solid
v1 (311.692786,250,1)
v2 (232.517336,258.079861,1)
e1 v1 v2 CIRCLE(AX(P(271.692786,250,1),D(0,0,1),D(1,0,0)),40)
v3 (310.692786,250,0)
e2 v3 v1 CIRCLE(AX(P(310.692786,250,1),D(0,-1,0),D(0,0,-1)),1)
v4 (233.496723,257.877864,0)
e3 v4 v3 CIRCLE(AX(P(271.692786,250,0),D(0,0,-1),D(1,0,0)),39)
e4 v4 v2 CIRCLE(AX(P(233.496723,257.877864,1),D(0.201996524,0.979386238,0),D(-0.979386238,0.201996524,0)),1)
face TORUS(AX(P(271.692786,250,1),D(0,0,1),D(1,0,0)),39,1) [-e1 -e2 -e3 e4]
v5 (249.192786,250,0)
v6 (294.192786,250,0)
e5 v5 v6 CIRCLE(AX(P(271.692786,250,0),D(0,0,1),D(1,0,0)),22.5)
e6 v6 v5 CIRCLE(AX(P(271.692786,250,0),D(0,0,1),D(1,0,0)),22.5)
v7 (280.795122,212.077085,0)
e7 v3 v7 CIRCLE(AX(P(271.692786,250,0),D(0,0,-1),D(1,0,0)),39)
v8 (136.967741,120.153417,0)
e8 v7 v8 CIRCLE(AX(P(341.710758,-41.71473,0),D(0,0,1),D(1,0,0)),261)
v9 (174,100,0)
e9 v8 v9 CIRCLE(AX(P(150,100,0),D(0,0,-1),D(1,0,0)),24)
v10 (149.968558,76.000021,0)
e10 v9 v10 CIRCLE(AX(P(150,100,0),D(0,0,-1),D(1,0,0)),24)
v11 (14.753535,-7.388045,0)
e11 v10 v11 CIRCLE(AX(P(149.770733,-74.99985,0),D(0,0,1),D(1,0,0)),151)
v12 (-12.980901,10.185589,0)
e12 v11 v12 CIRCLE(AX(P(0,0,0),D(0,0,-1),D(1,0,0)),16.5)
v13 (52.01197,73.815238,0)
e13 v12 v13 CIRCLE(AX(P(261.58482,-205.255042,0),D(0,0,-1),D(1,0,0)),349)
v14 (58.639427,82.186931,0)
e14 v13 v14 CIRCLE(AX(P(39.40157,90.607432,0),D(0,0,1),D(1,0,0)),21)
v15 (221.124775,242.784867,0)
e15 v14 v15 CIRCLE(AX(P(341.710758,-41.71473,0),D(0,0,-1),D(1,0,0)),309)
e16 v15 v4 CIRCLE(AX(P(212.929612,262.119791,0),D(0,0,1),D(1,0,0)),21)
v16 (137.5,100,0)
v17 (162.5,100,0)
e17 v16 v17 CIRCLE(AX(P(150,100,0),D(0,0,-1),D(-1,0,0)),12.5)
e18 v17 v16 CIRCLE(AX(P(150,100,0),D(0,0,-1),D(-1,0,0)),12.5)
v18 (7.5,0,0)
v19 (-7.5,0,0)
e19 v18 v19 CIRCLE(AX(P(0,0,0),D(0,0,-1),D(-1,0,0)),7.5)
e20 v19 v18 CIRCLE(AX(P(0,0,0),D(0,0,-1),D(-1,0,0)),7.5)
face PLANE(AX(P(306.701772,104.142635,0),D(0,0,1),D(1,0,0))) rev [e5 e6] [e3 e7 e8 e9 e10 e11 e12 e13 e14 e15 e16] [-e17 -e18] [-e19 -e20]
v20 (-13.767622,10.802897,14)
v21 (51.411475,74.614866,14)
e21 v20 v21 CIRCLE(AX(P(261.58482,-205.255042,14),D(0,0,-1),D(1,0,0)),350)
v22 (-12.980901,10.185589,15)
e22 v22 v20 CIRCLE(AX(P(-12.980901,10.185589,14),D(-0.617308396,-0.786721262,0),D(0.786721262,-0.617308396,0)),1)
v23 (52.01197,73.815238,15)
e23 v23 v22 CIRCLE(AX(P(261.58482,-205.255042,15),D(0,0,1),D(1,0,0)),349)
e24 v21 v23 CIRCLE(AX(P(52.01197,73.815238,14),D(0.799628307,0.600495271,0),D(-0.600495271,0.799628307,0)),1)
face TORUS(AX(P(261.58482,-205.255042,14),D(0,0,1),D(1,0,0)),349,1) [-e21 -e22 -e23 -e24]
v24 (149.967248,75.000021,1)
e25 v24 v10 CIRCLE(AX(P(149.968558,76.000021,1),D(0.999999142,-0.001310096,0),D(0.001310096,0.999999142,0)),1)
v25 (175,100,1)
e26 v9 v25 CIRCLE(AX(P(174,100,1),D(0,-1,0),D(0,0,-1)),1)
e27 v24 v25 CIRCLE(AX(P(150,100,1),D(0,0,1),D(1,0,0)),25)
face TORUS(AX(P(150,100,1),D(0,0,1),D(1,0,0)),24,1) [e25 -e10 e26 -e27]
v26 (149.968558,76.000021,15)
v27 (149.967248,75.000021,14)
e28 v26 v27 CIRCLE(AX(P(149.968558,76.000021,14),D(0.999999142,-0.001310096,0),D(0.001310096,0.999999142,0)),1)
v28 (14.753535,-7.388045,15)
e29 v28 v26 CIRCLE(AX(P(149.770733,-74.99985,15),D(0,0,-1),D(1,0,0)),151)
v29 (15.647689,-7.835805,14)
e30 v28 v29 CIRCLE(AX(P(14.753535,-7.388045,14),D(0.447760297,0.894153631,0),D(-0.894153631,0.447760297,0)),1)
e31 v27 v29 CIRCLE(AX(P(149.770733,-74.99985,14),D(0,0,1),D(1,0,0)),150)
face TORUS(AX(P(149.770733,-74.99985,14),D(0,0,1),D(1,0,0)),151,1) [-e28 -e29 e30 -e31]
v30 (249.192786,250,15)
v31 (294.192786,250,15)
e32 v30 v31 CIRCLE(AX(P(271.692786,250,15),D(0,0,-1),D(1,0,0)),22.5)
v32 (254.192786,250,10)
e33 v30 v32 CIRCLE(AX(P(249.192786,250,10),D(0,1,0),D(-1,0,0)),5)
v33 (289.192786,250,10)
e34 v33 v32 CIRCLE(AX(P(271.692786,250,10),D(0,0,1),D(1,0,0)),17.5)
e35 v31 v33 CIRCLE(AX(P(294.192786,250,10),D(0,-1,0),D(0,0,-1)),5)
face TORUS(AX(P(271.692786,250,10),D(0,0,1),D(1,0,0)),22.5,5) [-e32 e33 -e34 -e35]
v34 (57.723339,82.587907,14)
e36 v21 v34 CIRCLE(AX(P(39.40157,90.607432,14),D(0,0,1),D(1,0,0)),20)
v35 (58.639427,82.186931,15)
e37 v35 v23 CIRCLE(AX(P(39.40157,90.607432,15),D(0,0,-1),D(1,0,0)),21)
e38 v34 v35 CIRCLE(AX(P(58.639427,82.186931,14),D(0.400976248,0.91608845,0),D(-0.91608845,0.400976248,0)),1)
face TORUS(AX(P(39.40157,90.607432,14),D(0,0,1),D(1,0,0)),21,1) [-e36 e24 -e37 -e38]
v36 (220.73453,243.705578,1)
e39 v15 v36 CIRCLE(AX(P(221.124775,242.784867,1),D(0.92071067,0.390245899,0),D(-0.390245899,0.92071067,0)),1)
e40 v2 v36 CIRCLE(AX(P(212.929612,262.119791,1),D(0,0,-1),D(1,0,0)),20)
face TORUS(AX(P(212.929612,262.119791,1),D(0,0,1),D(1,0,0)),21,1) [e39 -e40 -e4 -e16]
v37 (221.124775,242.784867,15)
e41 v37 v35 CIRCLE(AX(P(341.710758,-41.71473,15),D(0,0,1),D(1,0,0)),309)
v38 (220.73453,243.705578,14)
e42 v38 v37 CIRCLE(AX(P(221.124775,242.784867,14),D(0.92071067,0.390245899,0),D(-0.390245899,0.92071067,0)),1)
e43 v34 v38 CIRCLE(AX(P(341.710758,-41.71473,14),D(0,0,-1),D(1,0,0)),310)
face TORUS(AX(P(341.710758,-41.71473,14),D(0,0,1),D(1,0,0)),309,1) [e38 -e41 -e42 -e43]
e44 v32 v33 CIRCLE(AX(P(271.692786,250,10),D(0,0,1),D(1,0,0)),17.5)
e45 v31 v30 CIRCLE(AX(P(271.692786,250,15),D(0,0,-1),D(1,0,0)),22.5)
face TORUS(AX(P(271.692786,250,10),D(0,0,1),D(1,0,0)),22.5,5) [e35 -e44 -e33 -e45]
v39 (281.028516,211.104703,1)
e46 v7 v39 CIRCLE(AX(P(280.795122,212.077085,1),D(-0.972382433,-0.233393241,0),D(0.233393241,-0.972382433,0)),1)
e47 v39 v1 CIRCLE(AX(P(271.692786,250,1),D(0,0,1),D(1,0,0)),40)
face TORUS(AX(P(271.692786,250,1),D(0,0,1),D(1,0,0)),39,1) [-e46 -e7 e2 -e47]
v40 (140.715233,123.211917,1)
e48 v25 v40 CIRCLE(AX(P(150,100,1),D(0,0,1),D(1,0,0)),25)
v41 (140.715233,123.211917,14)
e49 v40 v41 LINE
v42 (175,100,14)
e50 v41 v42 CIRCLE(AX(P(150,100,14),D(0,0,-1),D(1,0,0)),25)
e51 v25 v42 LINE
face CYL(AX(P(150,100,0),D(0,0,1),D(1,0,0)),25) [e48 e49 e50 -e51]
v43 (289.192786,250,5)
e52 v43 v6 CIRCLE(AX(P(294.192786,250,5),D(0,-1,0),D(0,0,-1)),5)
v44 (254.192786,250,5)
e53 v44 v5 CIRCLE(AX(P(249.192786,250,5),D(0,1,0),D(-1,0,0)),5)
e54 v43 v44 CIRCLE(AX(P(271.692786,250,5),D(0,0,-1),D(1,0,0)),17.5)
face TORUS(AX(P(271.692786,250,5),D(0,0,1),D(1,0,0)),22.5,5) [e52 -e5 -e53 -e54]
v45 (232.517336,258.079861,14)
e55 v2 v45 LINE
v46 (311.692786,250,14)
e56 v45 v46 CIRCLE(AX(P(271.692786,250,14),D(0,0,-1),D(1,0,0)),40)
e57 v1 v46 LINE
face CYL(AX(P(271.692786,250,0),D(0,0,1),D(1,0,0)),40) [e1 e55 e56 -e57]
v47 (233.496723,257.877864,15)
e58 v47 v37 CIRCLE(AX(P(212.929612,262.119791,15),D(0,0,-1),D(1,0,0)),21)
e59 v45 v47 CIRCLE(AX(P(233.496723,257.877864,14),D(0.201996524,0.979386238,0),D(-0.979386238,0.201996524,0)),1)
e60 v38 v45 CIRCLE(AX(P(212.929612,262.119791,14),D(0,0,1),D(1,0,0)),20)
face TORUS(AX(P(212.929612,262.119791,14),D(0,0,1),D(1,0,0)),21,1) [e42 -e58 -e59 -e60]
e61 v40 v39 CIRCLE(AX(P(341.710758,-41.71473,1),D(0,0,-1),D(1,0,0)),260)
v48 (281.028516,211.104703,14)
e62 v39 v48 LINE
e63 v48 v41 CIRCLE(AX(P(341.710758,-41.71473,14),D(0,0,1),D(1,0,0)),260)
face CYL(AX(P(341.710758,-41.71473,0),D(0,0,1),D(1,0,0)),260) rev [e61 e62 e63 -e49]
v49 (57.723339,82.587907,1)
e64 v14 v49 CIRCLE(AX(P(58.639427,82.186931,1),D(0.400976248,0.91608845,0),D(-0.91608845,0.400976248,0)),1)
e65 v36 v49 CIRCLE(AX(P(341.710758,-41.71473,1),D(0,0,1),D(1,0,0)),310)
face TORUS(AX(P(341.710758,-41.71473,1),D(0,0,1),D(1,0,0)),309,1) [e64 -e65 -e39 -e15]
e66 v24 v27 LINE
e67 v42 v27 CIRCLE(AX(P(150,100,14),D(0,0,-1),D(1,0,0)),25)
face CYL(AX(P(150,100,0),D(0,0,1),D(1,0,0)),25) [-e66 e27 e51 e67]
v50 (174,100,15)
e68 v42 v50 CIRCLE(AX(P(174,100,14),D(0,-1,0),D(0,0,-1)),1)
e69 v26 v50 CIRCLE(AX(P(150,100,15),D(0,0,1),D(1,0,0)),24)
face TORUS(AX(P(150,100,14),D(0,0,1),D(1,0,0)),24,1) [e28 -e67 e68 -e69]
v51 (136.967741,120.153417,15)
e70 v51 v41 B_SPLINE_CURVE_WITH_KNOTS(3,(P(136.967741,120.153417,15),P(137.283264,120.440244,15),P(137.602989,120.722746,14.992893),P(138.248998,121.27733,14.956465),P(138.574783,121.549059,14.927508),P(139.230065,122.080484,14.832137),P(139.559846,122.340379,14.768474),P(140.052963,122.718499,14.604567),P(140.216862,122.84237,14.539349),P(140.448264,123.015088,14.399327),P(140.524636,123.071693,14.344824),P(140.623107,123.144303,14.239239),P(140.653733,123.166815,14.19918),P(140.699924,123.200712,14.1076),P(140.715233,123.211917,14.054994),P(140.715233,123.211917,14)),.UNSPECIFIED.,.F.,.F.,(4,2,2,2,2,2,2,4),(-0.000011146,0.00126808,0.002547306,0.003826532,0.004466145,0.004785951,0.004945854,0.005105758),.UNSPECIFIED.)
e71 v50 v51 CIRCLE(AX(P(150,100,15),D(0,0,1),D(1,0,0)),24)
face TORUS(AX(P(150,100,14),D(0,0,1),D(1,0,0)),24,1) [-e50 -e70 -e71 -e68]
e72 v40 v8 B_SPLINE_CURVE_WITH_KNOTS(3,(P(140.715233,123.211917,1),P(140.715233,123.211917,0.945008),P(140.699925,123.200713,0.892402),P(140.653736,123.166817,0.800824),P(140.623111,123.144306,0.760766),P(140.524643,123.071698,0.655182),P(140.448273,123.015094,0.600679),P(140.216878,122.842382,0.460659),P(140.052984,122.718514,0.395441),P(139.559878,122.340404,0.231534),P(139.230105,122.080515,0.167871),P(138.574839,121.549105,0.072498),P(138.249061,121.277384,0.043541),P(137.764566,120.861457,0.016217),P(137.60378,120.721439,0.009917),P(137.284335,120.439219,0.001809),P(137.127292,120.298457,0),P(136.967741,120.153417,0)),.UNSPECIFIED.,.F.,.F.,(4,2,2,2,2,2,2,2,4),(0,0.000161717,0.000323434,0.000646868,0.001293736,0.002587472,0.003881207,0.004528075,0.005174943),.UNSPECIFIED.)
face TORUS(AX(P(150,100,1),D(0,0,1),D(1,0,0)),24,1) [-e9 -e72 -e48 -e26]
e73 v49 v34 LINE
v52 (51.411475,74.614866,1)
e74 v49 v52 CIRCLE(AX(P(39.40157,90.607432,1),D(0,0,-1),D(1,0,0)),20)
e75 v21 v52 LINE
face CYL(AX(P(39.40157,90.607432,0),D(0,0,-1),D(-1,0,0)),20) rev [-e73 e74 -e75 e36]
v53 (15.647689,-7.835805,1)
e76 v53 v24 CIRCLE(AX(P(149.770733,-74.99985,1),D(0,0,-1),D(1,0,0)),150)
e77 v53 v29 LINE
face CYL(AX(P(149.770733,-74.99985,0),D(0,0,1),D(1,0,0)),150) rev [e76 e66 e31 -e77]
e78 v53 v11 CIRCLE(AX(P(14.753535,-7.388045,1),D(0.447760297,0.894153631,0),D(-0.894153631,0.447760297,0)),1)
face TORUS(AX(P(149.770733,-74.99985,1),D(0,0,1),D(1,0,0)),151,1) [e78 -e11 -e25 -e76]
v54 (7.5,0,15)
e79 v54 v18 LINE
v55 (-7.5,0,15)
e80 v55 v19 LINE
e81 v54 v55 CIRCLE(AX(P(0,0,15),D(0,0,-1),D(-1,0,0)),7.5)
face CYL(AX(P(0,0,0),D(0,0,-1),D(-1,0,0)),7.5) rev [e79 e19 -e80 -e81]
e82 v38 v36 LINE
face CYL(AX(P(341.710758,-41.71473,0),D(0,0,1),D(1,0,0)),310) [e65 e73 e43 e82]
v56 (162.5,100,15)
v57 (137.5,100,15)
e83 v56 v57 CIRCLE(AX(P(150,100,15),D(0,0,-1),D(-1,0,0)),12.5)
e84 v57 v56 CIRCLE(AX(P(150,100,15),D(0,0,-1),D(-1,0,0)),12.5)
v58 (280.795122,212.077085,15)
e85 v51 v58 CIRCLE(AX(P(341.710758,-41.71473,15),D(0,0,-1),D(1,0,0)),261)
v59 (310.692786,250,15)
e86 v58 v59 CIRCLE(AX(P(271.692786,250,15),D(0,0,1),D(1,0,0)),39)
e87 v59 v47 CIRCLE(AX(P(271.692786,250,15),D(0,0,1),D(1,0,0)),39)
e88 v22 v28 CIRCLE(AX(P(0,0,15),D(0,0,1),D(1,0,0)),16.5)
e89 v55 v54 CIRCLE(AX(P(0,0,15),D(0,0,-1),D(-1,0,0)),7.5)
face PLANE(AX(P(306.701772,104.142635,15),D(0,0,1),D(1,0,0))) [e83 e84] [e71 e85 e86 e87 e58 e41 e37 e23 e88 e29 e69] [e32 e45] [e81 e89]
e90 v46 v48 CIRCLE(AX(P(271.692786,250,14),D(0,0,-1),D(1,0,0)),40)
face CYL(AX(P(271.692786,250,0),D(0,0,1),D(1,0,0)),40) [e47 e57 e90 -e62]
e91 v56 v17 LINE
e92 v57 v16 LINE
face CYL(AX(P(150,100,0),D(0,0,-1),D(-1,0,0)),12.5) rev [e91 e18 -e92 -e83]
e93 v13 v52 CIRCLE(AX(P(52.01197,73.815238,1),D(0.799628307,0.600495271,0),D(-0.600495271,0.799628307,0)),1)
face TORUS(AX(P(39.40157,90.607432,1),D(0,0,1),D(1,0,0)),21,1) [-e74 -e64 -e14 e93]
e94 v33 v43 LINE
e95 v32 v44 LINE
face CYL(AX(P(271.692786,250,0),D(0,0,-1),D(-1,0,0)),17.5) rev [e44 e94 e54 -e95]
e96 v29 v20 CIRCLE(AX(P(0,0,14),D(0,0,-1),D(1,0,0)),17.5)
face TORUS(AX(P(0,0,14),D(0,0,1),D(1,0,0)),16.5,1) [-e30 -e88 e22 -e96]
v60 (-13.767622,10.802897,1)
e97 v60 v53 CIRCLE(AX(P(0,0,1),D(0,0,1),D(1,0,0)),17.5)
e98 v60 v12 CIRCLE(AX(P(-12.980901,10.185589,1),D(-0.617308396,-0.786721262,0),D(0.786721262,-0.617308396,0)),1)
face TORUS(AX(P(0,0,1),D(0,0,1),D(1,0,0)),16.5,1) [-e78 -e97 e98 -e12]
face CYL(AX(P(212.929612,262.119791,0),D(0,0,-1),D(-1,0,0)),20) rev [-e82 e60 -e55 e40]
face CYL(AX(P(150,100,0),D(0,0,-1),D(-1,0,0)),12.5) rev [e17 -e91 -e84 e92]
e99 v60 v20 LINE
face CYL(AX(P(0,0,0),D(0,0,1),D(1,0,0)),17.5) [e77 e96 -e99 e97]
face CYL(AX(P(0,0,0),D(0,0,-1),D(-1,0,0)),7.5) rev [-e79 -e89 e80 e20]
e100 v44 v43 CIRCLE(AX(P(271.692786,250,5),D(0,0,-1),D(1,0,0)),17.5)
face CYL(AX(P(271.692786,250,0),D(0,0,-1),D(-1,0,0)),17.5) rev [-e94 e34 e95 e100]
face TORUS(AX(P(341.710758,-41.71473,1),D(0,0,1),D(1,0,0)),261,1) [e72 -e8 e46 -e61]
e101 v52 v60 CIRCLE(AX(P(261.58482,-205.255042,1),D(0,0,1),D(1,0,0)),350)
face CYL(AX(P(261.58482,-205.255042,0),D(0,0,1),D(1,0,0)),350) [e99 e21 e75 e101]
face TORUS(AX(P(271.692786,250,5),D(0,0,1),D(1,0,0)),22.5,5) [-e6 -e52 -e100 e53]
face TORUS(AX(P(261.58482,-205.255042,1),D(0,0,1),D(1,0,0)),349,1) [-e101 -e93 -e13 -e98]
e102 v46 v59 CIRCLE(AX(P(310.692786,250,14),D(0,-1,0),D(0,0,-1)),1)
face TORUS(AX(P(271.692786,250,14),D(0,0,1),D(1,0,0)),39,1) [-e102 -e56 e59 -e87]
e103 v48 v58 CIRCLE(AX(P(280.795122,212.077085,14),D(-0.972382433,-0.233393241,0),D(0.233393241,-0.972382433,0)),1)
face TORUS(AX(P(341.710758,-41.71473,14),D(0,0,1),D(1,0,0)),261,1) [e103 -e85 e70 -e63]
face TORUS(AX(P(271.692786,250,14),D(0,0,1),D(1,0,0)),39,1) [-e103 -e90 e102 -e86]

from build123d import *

# Parameters (mm, degrees)
BOSS_EXTRUDE1_DEPTH        = 15
M30_CLEARANCE_HOLE1_D      = 35
F_25_0_25_DIAMETER_HOLE1_D = 25
F_15_0_15_DIAMETER_HOLE1_D = 15
FILLET1_R                  = 20
FILLET2_R                  = 1
FILLET3_R                  = 5


with BuildPart() as part:
    # Sketch1 → Boss-Extrude1 (new body)
    with BuildSketch(Plane.XY.offset(15)):
        with BuildLine():
            ThreePointArc((231.736862835, 248.122711482), (126.150277633, 181.071444034), (55.655412109, 77.752165214))
            ThreePointArc((55.655412109, 77.752165214), (18.626786765, 46.68025613), (-13.767622093, 10.802896922))
            ThreePointArc((-13.767622093, 10.802896922), (-9.366641165, -14.782287823), (15.647688545, -7.835805205))
            ThreePointArc((15.647688545, -7.835805205), (71.03368715, 52.673473852), (149.967247602, 75.000021454))
            ThreePointArc((149.967247602, 75.000021454), (174.552001265, 104.711606298), (140.715233091, 123.211917272))
            ThreePointArc((140.715233091, 123.211917272), (203.688662251, 178.625691043), (281.028515533, 211.104702698))
            ThreePointArc((281.028515533, 211.104702698), (295.713241867, 281.984647802), (231.736862835, 248.122711482))
        make_face()
    extrude(amount=-BOSS_EXTRUDE1_DEPTH)

    # M30 Clearance Hole1 (through all)
    with Locations(Plane(origin=(0, 0, 0), x_dir=(-1, 0, 0), z_dir=(0, 0, -1))):
        with Locations((-271.692785898, 250)):
            Hole(M30_CLEARANCE_HOLE1_D / 2)

    # Ø25.0 (25) Diameter Hole1 (through all)
    with Locations(Plane(origin=(0, 0, 0), x_dir=(-1, 0, 0), z_dir=(0, 0, -1))):
        with Locations((-150, 100)):
            Hole(F_25_0_25_DIAMETER_HOLE1_D / 2)

    # Ø15.0 (15) Diameter Hole1 (through all)
    with Locations(Plane(origin=(0, 0, 0), x_dir=(-1, 0, 0), z_dir=(0, 0, -1))):
        with Locations((0, 0)):
            Hole(F_15_0_15_DIAMETER_HOLE1_D / 2)

    # Fillet1
    fillet1_edges = [part.edges().sort_by_distance(p)[0] for p in [
        (55.655412109, 77.752165214, 7.5),
        (231.736862835, 248.122711482, 7.5),
    ]]
    fillet(fillet1_edges, radius=FILLET1_R)

    # Fillet2
    fillet2_edges = [part.edges().sort_by_distance(p)[0] for p in [
        (299.518468185, 278.735542543, 15),
        (-9.366641165, -14.782287823, 0),
        (71.03368715, 52.673473852, 0),
        (174.552001265, 104.711606298, 0),
        (203.688662251, 178.625691043, 0),
        (123.791931468, 178.765167219, 15),
        (123.791931468, 178.765167219, 0),
        (16.734224094, 44.841311513, 15),
        (16.734224094, 44.841311513, 0),
        (228.397133093, 249.440841249, 15),
        (228.397133093, 249.440841249, 0),
        (55.082608051, 78.193527318, 15),
        (55.082608051, 78.193527318, 0),
        (299.518468185, 278.735542543, 0),
        (203.688662251, 178.625691043, 15),
        (174.552001265, 104.711606298, 15),
        (71.03368715, 52.673473852, 15),
        (-9.366641165, -14.782287823, 15),
    ]]
    fillet(fillet2_edges, radius=FILLET2_R)

    # Fillet3
    fillet3_edges = [part.edges().sort_by_distance(p)[0] for p in [
        (254.192785898, 250, 0),
        (254.192785898, 250, 15),
    ]]
    fillet(fillet3_edges, radius=FILLET3_R)


solid = part.part
